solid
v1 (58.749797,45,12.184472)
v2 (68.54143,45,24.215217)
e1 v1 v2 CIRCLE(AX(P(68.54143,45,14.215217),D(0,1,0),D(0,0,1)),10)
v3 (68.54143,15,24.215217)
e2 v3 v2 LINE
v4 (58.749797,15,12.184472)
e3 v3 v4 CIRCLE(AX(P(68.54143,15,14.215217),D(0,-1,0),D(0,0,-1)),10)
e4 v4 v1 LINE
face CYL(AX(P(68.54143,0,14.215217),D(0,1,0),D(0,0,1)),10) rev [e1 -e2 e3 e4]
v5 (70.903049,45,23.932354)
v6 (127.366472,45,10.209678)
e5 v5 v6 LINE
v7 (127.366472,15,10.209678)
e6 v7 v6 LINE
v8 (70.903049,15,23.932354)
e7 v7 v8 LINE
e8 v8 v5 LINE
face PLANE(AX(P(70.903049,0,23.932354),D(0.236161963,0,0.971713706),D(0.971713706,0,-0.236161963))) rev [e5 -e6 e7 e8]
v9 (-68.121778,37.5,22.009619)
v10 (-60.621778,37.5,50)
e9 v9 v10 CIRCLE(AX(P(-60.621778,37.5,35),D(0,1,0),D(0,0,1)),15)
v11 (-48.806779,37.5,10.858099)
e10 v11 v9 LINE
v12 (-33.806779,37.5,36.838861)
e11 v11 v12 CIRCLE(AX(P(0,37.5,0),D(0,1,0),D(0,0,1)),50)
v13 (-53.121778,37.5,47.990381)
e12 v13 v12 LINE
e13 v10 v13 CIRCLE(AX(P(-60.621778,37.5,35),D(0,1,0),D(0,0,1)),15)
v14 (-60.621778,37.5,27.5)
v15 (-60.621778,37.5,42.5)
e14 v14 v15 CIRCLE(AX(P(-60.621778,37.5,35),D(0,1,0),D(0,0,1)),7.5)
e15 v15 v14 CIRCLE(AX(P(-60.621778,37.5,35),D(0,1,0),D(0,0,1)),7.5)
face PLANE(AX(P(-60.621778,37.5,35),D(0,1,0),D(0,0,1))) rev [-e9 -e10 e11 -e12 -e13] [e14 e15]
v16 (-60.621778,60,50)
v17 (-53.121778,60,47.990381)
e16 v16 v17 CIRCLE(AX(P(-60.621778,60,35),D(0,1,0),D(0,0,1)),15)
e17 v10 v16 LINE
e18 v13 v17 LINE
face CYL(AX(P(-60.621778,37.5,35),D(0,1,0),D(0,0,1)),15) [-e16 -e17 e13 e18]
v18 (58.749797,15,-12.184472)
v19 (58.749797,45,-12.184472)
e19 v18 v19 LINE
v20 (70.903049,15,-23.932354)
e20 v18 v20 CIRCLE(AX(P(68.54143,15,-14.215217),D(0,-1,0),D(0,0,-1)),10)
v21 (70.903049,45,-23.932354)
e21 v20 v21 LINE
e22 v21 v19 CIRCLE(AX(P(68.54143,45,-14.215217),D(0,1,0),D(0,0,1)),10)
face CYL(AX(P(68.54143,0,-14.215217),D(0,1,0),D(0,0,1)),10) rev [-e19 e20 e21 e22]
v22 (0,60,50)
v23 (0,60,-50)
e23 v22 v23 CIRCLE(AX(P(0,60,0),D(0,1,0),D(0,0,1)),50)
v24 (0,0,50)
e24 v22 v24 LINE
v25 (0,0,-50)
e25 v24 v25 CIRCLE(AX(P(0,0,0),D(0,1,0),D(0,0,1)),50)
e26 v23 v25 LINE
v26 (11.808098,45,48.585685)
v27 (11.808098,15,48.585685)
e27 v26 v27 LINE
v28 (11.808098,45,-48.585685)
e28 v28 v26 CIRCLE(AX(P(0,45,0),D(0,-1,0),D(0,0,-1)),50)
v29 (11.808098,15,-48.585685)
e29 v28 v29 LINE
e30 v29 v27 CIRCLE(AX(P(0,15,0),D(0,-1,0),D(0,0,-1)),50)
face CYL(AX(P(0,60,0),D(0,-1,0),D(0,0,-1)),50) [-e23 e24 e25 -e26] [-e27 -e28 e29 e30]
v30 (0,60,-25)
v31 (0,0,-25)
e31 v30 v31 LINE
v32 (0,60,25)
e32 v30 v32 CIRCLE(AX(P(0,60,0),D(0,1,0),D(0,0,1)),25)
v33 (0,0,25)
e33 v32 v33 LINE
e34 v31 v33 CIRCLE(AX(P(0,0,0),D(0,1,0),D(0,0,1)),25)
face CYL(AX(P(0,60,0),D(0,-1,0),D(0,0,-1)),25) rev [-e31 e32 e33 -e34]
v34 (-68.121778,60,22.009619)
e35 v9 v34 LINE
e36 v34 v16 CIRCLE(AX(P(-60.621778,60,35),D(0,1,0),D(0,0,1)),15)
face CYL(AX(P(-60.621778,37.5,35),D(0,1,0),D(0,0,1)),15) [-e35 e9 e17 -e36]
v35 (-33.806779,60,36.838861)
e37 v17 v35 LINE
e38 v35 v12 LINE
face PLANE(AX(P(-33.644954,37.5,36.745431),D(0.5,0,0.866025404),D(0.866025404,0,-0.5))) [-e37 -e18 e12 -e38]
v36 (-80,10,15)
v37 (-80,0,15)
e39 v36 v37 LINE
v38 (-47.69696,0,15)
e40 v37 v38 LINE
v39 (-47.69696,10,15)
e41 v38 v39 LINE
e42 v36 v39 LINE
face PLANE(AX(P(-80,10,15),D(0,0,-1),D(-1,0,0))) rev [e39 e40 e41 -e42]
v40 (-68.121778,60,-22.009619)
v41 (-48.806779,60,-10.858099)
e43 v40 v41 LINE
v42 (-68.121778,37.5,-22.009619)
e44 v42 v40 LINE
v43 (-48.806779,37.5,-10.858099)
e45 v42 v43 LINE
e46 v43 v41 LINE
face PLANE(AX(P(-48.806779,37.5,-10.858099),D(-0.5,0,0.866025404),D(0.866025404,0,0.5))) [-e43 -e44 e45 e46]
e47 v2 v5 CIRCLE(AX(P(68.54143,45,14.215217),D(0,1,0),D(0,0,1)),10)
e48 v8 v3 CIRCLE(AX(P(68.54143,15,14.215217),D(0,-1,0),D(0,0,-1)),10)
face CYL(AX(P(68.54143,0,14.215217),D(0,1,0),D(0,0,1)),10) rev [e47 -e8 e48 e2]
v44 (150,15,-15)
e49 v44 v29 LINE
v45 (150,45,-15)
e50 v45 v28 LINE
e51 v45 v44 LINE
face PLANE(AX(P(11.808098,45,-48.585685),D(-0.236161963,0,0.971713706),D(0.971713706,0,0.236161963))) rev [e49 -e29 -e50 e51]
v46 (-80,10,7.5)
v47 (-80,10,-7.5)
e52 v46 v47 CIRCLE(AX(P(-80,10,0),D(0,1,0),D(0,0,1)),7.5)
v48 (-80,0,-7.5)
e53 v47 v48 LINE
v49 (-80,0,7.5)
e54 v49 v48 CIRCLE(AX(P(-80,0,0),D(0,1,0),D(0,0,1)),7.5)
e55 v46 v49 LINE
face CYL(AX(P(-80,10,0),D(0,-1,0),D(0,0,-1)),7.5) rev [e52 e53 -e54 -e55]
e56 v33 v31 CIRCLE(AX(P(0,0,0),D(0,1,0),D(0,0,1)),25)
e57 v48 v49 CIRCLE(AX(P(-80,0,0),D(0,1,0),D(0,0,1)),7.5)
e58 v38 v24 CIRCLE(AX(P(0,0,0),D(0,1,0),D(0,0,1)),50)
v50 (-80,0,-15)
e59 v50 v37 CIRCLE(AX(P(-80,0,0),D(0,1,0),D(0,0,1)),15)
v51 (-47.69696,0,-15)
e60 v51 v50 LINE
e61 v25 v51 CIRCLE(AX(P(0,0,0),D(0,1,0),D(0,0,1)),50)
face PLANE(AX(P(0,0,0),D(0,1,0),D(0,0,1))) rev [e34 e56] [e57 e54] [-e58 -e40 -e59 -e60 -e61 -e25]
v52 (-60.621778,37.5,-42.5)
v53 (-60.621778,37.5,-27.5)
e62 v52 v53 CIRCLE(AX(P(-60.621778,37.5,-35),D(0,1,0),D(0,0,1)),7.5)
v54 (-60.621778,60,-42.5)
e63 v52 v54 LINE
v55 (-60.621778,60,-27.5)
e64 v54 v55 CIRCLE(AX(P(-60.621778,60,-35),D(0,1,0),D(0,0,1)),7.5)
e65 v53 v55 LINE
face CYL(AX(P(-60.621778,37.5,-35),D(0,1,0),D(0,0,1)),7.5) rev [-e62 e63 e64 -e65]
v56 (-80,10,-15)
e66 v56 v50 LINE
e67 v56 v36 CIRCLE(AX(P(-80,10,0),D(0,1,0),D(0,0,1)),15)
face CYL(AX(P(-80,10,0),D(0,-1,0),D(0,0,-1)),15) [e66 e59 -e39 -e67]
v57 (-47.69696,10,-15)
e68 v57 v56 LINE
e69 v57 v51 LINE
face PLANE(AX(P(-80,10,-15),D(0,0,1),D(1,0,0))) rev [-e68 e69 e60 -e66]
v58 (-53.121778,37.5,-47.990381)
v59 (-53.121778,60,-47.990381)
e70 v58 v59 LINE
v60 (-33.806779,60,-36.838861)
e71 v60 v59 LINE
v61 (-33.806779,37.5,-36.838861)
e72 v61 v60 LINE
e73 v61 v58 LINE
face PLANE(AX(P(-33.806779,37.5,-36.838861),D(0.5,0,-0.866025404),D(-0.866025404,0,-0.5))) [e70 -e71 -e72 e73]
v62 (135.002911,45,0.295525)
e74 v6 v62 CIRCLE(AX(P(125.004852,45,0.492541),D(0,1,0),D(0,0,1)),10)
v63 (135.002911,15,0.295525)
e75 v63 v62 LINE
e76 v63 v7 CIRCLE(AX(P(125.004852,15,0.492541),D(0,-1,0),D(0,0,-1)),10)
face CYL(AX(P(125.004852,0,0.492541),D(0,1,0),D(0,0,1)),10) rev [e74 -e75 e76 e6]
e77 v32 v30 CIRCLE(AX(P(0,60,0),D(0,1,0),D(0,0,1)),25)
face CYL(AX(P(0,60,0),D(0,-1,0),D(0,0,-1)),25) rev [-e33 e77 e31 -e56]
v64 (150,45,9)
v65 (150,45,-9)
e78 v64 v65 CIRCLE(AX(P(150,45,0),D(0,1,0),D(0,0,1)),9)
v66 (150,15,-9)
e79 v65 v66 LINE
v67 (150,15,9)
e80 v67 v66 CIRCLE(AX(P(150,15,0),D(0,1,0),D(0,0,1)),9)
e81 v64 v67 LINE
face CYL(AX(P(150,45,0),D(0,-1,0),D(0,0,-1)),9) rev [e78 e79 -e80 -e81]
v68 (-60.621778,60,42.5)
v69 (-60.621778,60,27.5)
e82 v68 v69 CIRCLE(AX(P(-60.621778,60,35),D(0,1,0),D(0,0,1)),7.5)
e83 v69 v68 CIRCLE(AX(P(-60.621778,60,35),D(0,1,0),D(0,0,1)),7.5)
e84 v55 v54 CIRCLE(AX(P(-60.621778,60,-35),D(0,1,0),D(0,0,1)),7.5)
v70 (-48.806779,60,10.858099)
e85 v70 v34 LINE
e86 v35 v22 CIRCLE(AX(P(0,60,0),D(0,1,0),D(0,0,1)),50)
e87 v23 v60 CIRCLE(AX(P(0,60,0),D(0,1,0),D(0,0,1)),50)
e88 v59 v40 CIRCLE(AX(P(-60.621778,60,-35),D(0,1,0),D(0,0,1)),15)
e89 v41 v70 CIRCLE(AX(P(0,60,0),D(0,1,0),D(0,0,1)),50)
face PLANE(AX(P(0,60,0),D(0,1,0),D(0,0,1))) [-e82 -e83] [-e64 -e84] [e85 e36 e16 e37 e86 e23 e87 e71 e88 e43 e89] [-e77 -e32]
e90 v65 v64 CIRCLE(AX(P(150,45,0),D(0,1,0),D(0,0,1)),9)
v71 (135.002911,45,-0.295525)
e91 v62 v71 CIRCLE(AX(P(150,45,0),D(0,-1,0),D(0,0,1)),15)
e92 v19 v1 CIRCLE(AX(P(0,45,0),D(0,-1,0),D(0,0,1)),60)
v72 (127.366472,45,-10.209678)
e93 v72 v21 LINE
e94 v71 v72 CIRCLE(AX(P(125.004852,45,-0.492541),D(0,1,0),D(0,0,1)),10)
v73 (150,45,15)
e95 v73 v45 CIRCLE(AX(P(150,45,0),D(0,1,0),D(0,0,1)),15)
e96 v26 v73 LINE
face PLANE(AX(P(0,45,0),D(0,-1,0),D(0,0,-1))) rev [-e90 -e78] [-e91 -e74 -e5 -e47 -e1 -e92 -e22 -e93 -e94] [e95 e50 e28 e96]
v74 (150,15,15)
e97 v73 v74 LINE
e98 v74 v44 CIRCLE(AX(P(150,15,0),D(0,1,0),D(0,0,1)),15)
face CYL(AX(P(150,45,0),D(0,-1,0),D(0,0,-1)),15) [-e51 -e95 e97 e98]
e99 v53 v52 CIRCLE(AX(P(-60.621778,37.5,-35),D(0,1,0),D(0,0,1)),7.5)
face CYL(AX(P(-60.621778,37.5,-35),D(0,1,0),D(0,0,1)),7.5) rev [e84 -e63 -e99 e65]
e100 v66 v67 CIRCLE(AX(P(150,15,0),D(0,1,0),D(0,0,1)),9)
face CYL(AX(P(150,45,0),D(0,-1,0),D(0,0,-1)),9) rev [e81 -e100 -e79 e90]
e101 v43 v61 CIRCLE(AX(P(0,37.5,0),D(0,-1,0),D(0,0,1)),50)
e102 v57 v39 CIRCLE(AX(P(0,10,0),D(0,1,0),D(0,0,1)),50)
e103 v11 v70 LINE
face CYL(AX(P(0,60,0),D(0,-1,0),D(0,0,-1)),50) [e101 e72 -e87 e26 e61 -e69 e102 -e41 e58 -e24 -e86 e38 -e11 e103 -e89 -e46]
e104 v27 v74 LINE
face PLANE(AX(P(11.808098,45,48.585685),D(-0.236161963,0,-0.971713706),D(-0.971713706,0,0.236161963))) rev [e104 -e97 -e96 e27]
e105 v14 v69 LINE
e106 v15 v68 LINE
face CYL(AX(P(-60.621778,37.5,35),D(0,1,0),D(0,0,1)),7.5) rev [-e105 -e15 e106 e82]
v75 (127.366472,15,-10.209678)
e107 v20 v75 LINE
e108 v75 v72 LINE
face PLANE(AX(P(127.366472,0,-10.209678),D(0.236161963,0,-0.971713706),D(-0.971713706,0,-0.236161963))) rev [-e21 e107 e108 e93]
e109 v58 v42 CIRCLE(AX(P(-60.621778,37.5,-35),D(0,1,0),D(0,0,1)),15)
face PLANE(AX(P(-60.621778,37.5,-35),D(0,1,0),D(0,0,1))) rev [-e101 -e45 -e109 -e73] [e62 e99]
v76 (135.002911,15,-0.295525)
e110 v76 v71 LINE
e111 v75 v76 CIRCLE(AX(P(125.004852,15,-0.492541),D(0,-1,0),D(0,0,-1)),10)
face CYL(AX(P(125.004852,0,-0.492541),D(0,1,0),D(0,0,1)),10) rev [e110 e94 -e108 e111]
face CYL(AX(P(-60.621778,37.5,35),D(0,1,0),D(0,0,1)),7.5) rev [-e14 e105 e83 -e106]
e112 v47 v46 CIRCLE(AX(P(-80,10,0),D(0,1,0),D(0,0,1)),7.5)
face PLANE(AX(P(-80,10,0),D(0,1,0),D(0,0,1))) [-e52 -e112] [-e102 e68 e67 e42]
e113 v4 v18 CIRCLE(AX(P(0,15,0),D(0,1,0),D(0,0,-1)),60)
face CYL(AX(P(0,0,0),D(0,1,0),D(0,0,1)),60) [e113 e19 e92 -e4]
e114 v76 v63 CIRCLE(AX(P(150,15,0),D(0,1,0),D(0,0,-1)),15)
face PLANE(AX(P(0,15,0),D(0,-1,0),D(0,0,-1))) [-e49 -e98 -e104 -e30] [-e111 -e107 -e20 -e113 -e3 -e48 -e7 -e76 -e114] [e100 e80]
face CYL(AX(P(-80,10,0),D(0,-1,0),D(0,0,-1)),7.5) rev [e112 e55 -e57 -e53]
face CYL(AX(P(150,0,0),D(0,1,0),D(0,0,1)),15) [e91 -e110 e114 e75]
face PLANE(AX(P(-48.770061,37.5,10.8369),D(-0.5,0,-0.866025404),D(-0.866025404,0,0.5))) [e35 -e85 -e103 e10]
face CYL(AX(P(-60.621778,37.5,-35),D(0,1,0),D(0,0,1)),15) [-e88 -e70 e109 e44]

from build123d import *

# Parameters (mm, degrees)
HUB_SKETCH_R                = 50
HUB_SKETCH_R_2              = 25
HUB_100_BORE_50_DEPTH       = 60
LEVER_ARM_SKETCH_R          = 9
LEVER_ARM_DEPTH             = 15
ARM_LIGHTENING_WINDOW_DEPTH = 179.185296812
EAR_A_SKETCH_R              = 7.5
MOUNTING_EAR_A_DEPTH        = 22.5
MOUNTING_START              = -22.5
EAR_B_SKETCH_R              = 7.5
MOUNTING_EAR_B_DEPTH        = 22.5
ARM_WEB_SKETCH_R            = 7.5
ARM_WEB_10MM_DEPTH          = 10


with BuildPart() as part:
    # Hub Sketch → Hub Ø100 Bore Ø50 (new body)
    with BuildSketch(Plane(origin=(0, 0, 0), x_dir=(1, 0, 0), z_dir=(0, 1, 0))):
        with Locations(Location((0, 0, 0), (0, 0, 270))):
            Circle(HUB_SKETCH_R)
        with Locations(Location((0, 0, 0), (0, 0, 270))):
            Circle(HUB_SKETCH_R_2, mode=Mode.SUBTRACT)
    extrude(amount=HUB_100_BORE_50_DEPTH)

    # Lever Arm Sketch → Lever Arm (add, symmetric)
    with BuildSketch(Plane(origin=(0, 30, 0), x_dir=(1, 0, 0), z_dir=(0, 1, 0))):
        with BuildLine():
            Line((11.808098134, 48.585685325), (150, 15))
            ThreePointArc((150, 15), (165, 0), (150, -15))
            Line((150, -15), (11.808098134, -48.585685325))
            ThreePointArc((11.808098134, -48.585685325), (50, 0), (11.808098134, 48.585685325))
        make_face()
        with Locations(Location((150, 0, 0), (0, 0, 270))):
            Circle(LEVER_ARM_SKETCH_R, mode=Mode.SUBTRACT)
    extrude(amount=LEVER_ARM_DEPTH, both=True)

    # Arm Window Sketch → Arm Lightening Window (cut, through all)
    with BuildSketch(Plane(origin=(0, 45, 0), x_dir=(1, 0, 0), z_dir=(0, 1, 0))):
        with BuildLine():
            Line((127.366472028, 10.209677932), (70.90304943, 23.932354284))
            ThreePointArc((70.90304943, 23.932354284), (61.591288857, 21.405178334), (58.749796974, 12.184471902))
            ThreePointArc((58.749796974, 12.184471902), (60, 0), (58.749796974, -12.184471902))
            ThreePointArc((58.749796974, -12.184471902), (61.591288857, -21.405178334), (70.90304943, -23.932354284))
            Line((70.90304943, -23.932354284), (127.366472028, -10.209677932))
            ThreePointArc((127.366472028, -10.209677932), (132.927164163, -6.594751643), (135.002911441, -0.29552452))
            ThreePointArc((135.002911441, -0.29552452), (135, 0), (135.002911441, 0.29552452))
            ThreePointArc((135.002911441, 0.29552452), (132.927164163, 6.594751643), (127.366472028, 10.209677932))
        make_face()
    extrude(amount=-ARM_LIGHTENING_WINDOW_DEPTH, mode=Mode.SUBTRACT)

    # Ear A Sketch → Mounting Ear A (add)
    with BuildSketch(Plane(origin=(0, 60, 0), x_dir=(1, 0, 0), z_dir=(0, 1, 0))):
        with BuildLine():
            Line((-48.770060726, -10.836899613), (-68.121778265, -22.009618943))
            ThreePointArc((-68.121778265, -22.009618943), (-73.612159322, -42.5), (-53.121778265, -47.990381057))
            Line((-53.121778265, -47.990381057), (-33.644953635, -36.745431114))
            ThreePointArc((-33.644953635, -36.745431114), (-43.203476292, -24.956389512), (-48.770060726, -10.836899613))
        make_face()
        with Locations(Location((-60.621778265, -35, 0), (0, 0, 270))):
            Circle(EAR_A_SKETCH_R, mode=Mode.SUBTRACT)
    extrude(amount=-MOUNTING_EAR_A_DEPTH)

    # Ear B Sketch → Mounting Ear B (add)
    with BuildSketch(Plane(origin=(0, 60, 0), x_dir=(1, 0, 0), z_dir=(0, 1, 0)).offset(MOUNTING_START)):
        with BuildLine():
            Line((-33.806779105, 36.838861092), (-53.121778265, 47.990381057))
            ThreePointArc((-53.121778265, 47.990381057), (-73.612159322, 42.5), (-68.121778265, 22.009618943))
            Line((-68.121778265, 22.009618943), (-48.806779105, 10.858098979))
            ThreePointArc((-48.806779105, 10.858098979), (-43.301270189, 25), (-33.806779105, 36.838861092))
        make_face()
        with Locations(Location((-60.621778265, 35, 0), (0, 0, 270))):
            Circle(EAR_B_SKETCH_R, mode=Mode.SUBTRACT)
    extrude(amount=MOUNTING_EAR_B_DEPTH)

    # Arm Web Sketch → Arm Web 10mm (add)
    with BuildSketch(Plane(origin=(0, 0, 0), x_dir=(1, 0, 0), z_dir=(0, 1, 0))):
        with BuildLine():
            Line((-80, 15), (-50.661233673, 15))
            Line((-50.661233673, 15), (-43.043702026, 15))
            Line((-43.043702026, 15), (-43.043702026, -15))
            Line((-43.043702026, -15), (-80, -15))
            ThreePointArc((-80, -15), (-95, 0), (-80, 15))
        make_face()
        with Locations(Location((-80, 0, 0), (0, 0, 270))):
            Circle(ARM_WEB_SKETCH_R, mode=Mode.SUBTRACT)
    extrude(amount=ARM_WEB_10MM_DEPTH)


solid = part.part
